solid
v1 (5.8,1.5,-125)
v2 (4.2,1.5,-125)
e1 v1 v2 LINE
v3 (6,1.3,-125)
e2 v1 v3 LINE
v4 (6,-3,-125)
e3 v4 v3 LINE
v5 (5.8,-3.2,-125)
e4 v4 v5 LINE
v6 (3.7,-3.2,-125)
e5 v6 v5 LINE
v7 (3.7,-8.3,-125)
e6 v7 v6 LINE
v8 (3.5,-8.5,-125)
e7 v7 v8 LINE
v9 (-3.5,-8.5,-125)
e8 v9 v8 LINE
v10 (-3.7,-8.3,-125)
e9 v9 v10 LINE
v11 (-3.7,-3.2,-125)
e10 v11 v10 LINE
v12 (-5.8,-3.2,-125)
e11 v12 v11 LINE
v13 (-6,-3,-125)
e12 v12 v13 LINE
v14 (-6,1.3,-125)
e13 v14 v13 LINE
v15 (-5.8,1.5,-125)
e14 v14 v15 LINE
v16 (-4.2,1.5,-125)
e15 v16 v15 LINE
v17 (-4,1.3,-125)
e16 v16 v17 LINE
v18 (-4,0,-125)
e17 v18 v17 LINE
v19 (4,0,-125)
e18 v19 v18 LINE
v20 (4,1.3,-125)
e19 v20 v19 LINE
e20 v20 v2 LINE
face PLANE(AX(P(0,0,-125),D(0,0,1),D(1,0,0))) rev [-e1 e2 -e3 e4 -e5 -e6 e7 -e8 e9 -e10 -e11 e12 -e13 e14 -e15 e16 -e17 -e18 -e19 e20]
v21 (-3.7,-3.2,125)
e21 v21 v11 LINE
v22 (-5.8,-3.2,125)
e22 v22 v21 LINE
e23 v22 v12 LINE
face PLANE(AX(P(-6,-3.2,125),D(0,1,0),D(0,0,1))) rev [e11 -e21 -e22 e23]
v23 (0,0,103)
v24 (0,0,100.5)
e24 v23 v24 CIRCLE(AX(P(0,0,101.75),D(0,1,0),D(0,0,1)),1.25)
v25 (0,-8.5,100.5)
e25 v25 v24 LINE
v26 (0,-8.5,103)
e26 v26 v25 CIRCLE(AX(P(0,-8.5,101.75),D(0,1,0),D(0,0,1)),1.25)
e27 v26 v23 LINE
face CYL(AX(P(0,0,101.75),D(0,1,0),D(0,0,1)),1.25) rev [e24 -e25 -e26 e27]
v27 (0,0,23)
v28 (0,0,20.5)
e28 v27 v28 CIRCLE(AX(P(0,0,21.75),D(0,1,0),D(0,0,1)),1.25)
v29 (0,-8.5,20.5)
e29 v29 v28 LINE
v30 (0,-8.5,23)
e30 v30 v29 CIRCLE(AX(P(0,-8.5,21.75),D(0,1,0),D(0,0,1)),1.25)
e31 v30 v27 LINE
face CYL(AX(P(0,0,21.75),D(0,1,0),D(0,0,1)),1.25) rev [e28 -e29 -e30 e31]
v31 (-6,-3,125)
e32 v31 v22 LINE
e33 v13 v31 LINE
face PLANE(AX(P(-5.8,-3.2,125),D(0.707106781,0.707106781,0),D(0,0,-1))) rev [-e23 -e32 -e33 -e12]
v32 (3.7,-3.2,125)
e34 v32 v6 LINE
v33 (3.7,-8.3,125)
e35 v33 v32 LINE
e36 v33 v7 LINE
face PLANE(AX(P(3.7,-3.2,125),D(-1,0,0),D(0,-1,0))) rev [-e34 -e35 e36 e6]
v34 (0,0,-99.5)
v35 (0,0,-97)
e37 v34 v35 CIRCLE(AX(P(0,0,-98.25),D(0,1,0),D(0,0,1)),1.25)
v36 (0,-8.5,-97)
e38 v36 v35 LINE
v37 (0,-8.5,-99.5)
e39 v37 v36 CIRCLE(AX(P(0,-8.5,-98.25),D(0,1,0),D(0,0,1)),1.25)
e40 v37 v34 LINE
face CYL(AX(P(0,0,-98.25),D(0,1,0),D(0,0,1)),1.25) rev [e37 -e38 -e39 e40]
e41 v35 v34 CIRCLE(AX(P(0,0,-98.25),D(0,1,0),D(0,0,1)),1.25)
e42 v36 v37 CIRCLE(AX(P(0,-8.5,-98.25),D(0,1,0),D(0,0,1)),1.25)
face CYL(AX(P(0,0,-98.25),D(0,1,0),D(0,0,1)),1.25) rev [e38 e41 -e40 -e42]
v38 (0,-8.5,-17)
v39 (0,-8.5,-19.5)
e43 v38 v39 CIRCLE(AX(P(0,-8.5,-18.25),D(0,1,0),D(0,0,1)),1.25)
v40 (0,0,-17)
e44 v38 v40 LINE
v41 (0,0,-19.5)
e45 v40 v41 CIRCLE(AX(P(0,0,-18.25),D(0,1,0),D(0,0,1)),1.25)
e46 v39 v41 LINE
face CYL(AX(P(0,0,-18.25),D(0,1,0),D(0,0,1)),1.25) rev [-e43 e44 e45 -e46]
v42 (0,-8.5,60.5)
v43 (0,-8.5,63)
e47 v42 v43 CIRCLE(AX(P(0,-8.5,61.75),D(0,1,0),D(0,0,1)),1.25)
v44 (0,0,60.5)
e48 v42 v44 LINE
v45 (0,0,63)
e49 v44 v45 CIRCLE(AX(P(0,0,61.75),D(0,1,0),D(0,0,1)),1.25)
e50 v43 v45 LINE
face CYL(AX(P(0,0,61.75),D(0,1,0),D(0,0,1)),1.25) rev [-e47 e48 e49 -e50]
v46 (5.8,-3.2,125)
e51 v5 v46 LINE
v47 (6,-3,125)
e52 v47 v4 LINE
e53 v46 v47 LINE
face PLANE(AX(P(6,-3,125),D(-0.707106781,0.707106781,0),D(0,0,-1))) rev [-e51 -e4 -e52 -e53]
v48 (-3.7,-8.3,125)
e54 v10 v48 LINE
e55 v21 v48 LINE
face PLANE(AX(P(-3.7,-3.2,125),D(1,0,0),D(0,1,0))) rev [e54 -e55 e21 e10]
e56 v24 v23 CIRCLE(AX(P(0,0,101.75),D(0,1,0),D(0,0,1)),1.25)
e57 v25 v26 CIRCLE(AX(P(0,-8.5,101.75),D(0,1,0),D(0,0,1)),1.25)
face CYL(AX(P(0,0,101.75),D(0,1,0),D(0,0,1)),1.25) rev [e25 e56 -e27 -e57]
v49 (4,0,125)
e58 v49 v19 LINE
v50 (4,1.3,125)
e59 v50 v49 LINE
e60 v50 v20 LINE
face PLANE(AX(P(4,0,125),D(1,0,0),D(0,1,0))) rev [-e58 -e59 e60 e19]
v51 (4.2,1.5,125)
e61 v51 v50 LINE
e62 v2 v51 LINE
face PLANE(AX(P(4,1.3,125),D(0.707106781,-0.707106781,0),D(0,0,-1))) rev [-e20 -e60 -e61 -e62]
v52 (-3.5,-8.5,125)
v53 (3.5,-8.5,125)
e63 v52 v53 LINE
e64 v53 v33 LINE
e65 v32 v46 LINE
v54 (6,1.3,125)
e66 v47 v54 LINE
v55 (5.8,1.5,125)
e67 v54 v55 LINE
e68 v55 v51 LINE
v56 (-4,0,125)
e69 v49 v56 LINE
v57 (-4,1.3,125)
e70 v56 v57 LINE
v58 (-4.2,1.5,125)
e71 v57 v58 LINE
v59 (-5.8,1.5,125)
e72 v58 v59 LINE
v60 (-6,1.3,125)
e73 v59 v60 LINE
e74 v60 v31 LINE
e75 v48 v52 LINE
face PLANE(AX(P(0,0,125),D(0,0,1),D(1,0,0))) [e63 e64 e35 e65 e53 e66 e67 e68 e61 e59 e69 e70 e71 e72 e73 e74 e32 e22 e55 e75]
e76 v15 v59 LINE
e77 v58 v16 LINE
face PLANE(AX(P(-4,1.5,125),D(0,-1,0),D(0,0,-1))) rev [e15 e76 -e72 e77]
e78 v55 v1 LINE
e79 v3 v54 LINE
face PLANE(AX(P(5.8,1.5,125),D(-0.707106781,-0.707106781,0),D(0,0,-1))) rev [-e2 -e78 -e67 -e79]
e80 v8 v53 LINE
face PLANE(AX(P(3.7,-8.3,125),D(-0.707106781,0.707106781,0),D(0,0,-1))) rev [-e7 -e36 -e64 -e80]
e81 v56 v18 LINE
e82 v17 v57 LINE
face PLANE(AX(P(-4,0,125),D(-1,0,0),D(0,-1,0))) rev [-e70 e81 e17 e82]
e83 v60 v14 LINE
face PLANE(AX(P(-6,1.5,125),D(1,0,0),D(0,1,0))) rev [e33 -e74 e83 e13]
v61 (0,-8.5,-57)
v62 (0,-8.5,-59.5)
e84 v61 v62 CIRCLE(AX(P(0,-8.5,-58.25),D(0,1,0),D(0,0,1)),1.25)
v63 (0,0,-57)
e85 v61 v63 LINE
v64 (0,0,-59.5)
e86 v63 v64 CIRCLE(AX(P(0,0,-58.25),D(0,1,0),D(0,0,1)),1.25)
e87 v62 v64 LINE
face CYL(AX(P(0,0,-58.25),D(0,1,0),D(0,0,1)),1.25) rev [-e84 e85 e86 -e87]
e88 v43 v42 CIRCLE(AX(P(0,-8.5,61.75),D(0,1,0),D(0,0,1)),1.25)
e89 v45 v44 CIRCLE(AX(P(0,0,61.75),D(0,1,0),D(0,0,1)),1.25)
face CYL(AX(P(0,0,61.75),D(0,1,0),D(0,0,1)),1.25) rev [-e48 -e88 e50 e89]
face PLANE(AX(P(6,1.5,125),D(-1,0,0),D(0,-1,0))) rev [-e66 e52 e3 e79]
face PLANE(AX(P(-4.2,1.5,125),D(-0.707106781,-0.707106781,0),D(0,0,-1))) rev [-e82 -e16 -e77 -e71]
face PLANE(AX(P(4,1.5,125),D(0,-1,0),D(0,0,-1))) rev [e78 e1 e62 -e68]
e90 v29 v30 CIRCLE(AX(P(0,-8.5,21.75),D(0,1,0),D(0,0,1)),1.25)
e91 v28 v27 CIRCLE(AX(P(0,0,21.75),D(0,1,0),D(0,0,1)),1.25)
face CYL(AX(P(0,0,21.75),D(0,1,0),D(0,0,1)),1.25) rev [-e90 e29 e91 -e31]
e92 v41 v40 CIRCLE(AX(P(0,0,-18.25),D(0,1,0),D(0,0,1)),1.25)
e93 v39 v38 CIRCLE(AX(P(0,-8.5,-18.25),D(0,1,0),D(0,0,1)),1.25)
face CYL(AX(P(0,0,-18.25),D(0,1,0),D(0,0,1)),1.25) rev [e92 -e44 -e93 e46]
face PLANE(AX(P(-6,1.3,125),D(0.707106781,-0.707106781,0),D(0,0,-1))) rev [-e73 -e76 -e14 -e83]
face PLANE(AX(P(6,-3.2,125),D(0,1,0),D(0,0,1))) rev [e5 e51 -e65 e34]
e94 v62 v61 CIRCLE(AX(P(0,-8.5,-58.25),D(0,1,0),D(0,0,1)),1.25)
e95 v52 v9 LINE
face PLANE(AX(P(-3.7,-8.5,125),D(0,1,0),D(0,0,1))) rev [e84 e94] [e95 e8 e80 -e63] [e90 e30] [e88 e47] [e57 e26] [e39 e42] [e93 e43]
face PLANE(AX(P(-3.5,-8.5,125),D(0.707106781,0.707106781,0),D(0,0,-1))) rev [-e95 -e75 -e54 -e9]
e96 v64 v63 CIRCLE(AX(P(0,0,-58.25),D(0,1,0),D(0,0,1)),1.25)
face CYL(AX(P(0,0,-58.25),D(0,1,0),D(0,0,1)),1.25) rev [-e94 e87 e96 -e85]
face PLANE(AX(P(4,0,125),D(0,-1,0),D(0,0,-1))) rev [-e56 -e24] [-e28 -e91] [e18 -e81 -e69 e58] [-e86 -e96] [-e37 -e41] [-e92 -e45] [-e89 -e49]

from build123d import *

# Parameters (mm, degrees)
BOSS_EXTRUDE1_DEPTH = 125
M3_TAPPED_HOLE1_D   = 2.5
CHAMFER1_SIZE       = 0.2
LPATTERN1_COUNT     = 6
LPATTERN1_PITCH     = 40


with BuildPart() as part:
    # Sketch1 → Boss-Extrude1 (new, symmetric)
    with BuildSketch(Plane.XY):
        Polygon((4, 0), (-4, 0), (-4, 1.5), (-6, 1.5), (-6, -3.2), (-3.7, -3.2), (-3.7, -8.5), (3.7, -8.5), (3.7, -3.2), (6, -3.2), (6, 1.5), (4, 1.5), align=None)
    extrude(amount=BOSS_EXTRUDE1_DEPTH, both=True)

    # M3 Tapped Hole1 (through all)
    with Locations(Plane(origin=(0, 0, 0), x_dir=(1, 0, 0), z_dir=(0, 1, 0))):
        with Locations((0, 98.25)):
            m3_tapped_hole1 = Hole(M3_TAPPED_HOLE1_D / 2)

    # Chamfer1
    chamfer1_edges = [part.edges().sort_by_distance(p)[0] for p in [
        (4, 1.5, 0),
        (6, 1.5, 0),
        (6, -3.2, 0),
        (3.7, -8.5, 0),
        (-3.7, -8.5, 0),
        (-6, -3.2, 0),
        (-6, 1.5, 0),
        (-4, 1.5, 0),
    ]]
    chamfer(chamfer1_edges, length=CHAMFER1_SIZE)

    # LPattern1: M3 Tapped Hole1 ×6
    with Locations(*[(0, 0, i * LPATTERN1_PITCH) for i in range(1, LPATTERN1_COUNT)]):
        add(m3_tapped_hole1, mode=Mode.SUBTRACT)


solid = part.part
